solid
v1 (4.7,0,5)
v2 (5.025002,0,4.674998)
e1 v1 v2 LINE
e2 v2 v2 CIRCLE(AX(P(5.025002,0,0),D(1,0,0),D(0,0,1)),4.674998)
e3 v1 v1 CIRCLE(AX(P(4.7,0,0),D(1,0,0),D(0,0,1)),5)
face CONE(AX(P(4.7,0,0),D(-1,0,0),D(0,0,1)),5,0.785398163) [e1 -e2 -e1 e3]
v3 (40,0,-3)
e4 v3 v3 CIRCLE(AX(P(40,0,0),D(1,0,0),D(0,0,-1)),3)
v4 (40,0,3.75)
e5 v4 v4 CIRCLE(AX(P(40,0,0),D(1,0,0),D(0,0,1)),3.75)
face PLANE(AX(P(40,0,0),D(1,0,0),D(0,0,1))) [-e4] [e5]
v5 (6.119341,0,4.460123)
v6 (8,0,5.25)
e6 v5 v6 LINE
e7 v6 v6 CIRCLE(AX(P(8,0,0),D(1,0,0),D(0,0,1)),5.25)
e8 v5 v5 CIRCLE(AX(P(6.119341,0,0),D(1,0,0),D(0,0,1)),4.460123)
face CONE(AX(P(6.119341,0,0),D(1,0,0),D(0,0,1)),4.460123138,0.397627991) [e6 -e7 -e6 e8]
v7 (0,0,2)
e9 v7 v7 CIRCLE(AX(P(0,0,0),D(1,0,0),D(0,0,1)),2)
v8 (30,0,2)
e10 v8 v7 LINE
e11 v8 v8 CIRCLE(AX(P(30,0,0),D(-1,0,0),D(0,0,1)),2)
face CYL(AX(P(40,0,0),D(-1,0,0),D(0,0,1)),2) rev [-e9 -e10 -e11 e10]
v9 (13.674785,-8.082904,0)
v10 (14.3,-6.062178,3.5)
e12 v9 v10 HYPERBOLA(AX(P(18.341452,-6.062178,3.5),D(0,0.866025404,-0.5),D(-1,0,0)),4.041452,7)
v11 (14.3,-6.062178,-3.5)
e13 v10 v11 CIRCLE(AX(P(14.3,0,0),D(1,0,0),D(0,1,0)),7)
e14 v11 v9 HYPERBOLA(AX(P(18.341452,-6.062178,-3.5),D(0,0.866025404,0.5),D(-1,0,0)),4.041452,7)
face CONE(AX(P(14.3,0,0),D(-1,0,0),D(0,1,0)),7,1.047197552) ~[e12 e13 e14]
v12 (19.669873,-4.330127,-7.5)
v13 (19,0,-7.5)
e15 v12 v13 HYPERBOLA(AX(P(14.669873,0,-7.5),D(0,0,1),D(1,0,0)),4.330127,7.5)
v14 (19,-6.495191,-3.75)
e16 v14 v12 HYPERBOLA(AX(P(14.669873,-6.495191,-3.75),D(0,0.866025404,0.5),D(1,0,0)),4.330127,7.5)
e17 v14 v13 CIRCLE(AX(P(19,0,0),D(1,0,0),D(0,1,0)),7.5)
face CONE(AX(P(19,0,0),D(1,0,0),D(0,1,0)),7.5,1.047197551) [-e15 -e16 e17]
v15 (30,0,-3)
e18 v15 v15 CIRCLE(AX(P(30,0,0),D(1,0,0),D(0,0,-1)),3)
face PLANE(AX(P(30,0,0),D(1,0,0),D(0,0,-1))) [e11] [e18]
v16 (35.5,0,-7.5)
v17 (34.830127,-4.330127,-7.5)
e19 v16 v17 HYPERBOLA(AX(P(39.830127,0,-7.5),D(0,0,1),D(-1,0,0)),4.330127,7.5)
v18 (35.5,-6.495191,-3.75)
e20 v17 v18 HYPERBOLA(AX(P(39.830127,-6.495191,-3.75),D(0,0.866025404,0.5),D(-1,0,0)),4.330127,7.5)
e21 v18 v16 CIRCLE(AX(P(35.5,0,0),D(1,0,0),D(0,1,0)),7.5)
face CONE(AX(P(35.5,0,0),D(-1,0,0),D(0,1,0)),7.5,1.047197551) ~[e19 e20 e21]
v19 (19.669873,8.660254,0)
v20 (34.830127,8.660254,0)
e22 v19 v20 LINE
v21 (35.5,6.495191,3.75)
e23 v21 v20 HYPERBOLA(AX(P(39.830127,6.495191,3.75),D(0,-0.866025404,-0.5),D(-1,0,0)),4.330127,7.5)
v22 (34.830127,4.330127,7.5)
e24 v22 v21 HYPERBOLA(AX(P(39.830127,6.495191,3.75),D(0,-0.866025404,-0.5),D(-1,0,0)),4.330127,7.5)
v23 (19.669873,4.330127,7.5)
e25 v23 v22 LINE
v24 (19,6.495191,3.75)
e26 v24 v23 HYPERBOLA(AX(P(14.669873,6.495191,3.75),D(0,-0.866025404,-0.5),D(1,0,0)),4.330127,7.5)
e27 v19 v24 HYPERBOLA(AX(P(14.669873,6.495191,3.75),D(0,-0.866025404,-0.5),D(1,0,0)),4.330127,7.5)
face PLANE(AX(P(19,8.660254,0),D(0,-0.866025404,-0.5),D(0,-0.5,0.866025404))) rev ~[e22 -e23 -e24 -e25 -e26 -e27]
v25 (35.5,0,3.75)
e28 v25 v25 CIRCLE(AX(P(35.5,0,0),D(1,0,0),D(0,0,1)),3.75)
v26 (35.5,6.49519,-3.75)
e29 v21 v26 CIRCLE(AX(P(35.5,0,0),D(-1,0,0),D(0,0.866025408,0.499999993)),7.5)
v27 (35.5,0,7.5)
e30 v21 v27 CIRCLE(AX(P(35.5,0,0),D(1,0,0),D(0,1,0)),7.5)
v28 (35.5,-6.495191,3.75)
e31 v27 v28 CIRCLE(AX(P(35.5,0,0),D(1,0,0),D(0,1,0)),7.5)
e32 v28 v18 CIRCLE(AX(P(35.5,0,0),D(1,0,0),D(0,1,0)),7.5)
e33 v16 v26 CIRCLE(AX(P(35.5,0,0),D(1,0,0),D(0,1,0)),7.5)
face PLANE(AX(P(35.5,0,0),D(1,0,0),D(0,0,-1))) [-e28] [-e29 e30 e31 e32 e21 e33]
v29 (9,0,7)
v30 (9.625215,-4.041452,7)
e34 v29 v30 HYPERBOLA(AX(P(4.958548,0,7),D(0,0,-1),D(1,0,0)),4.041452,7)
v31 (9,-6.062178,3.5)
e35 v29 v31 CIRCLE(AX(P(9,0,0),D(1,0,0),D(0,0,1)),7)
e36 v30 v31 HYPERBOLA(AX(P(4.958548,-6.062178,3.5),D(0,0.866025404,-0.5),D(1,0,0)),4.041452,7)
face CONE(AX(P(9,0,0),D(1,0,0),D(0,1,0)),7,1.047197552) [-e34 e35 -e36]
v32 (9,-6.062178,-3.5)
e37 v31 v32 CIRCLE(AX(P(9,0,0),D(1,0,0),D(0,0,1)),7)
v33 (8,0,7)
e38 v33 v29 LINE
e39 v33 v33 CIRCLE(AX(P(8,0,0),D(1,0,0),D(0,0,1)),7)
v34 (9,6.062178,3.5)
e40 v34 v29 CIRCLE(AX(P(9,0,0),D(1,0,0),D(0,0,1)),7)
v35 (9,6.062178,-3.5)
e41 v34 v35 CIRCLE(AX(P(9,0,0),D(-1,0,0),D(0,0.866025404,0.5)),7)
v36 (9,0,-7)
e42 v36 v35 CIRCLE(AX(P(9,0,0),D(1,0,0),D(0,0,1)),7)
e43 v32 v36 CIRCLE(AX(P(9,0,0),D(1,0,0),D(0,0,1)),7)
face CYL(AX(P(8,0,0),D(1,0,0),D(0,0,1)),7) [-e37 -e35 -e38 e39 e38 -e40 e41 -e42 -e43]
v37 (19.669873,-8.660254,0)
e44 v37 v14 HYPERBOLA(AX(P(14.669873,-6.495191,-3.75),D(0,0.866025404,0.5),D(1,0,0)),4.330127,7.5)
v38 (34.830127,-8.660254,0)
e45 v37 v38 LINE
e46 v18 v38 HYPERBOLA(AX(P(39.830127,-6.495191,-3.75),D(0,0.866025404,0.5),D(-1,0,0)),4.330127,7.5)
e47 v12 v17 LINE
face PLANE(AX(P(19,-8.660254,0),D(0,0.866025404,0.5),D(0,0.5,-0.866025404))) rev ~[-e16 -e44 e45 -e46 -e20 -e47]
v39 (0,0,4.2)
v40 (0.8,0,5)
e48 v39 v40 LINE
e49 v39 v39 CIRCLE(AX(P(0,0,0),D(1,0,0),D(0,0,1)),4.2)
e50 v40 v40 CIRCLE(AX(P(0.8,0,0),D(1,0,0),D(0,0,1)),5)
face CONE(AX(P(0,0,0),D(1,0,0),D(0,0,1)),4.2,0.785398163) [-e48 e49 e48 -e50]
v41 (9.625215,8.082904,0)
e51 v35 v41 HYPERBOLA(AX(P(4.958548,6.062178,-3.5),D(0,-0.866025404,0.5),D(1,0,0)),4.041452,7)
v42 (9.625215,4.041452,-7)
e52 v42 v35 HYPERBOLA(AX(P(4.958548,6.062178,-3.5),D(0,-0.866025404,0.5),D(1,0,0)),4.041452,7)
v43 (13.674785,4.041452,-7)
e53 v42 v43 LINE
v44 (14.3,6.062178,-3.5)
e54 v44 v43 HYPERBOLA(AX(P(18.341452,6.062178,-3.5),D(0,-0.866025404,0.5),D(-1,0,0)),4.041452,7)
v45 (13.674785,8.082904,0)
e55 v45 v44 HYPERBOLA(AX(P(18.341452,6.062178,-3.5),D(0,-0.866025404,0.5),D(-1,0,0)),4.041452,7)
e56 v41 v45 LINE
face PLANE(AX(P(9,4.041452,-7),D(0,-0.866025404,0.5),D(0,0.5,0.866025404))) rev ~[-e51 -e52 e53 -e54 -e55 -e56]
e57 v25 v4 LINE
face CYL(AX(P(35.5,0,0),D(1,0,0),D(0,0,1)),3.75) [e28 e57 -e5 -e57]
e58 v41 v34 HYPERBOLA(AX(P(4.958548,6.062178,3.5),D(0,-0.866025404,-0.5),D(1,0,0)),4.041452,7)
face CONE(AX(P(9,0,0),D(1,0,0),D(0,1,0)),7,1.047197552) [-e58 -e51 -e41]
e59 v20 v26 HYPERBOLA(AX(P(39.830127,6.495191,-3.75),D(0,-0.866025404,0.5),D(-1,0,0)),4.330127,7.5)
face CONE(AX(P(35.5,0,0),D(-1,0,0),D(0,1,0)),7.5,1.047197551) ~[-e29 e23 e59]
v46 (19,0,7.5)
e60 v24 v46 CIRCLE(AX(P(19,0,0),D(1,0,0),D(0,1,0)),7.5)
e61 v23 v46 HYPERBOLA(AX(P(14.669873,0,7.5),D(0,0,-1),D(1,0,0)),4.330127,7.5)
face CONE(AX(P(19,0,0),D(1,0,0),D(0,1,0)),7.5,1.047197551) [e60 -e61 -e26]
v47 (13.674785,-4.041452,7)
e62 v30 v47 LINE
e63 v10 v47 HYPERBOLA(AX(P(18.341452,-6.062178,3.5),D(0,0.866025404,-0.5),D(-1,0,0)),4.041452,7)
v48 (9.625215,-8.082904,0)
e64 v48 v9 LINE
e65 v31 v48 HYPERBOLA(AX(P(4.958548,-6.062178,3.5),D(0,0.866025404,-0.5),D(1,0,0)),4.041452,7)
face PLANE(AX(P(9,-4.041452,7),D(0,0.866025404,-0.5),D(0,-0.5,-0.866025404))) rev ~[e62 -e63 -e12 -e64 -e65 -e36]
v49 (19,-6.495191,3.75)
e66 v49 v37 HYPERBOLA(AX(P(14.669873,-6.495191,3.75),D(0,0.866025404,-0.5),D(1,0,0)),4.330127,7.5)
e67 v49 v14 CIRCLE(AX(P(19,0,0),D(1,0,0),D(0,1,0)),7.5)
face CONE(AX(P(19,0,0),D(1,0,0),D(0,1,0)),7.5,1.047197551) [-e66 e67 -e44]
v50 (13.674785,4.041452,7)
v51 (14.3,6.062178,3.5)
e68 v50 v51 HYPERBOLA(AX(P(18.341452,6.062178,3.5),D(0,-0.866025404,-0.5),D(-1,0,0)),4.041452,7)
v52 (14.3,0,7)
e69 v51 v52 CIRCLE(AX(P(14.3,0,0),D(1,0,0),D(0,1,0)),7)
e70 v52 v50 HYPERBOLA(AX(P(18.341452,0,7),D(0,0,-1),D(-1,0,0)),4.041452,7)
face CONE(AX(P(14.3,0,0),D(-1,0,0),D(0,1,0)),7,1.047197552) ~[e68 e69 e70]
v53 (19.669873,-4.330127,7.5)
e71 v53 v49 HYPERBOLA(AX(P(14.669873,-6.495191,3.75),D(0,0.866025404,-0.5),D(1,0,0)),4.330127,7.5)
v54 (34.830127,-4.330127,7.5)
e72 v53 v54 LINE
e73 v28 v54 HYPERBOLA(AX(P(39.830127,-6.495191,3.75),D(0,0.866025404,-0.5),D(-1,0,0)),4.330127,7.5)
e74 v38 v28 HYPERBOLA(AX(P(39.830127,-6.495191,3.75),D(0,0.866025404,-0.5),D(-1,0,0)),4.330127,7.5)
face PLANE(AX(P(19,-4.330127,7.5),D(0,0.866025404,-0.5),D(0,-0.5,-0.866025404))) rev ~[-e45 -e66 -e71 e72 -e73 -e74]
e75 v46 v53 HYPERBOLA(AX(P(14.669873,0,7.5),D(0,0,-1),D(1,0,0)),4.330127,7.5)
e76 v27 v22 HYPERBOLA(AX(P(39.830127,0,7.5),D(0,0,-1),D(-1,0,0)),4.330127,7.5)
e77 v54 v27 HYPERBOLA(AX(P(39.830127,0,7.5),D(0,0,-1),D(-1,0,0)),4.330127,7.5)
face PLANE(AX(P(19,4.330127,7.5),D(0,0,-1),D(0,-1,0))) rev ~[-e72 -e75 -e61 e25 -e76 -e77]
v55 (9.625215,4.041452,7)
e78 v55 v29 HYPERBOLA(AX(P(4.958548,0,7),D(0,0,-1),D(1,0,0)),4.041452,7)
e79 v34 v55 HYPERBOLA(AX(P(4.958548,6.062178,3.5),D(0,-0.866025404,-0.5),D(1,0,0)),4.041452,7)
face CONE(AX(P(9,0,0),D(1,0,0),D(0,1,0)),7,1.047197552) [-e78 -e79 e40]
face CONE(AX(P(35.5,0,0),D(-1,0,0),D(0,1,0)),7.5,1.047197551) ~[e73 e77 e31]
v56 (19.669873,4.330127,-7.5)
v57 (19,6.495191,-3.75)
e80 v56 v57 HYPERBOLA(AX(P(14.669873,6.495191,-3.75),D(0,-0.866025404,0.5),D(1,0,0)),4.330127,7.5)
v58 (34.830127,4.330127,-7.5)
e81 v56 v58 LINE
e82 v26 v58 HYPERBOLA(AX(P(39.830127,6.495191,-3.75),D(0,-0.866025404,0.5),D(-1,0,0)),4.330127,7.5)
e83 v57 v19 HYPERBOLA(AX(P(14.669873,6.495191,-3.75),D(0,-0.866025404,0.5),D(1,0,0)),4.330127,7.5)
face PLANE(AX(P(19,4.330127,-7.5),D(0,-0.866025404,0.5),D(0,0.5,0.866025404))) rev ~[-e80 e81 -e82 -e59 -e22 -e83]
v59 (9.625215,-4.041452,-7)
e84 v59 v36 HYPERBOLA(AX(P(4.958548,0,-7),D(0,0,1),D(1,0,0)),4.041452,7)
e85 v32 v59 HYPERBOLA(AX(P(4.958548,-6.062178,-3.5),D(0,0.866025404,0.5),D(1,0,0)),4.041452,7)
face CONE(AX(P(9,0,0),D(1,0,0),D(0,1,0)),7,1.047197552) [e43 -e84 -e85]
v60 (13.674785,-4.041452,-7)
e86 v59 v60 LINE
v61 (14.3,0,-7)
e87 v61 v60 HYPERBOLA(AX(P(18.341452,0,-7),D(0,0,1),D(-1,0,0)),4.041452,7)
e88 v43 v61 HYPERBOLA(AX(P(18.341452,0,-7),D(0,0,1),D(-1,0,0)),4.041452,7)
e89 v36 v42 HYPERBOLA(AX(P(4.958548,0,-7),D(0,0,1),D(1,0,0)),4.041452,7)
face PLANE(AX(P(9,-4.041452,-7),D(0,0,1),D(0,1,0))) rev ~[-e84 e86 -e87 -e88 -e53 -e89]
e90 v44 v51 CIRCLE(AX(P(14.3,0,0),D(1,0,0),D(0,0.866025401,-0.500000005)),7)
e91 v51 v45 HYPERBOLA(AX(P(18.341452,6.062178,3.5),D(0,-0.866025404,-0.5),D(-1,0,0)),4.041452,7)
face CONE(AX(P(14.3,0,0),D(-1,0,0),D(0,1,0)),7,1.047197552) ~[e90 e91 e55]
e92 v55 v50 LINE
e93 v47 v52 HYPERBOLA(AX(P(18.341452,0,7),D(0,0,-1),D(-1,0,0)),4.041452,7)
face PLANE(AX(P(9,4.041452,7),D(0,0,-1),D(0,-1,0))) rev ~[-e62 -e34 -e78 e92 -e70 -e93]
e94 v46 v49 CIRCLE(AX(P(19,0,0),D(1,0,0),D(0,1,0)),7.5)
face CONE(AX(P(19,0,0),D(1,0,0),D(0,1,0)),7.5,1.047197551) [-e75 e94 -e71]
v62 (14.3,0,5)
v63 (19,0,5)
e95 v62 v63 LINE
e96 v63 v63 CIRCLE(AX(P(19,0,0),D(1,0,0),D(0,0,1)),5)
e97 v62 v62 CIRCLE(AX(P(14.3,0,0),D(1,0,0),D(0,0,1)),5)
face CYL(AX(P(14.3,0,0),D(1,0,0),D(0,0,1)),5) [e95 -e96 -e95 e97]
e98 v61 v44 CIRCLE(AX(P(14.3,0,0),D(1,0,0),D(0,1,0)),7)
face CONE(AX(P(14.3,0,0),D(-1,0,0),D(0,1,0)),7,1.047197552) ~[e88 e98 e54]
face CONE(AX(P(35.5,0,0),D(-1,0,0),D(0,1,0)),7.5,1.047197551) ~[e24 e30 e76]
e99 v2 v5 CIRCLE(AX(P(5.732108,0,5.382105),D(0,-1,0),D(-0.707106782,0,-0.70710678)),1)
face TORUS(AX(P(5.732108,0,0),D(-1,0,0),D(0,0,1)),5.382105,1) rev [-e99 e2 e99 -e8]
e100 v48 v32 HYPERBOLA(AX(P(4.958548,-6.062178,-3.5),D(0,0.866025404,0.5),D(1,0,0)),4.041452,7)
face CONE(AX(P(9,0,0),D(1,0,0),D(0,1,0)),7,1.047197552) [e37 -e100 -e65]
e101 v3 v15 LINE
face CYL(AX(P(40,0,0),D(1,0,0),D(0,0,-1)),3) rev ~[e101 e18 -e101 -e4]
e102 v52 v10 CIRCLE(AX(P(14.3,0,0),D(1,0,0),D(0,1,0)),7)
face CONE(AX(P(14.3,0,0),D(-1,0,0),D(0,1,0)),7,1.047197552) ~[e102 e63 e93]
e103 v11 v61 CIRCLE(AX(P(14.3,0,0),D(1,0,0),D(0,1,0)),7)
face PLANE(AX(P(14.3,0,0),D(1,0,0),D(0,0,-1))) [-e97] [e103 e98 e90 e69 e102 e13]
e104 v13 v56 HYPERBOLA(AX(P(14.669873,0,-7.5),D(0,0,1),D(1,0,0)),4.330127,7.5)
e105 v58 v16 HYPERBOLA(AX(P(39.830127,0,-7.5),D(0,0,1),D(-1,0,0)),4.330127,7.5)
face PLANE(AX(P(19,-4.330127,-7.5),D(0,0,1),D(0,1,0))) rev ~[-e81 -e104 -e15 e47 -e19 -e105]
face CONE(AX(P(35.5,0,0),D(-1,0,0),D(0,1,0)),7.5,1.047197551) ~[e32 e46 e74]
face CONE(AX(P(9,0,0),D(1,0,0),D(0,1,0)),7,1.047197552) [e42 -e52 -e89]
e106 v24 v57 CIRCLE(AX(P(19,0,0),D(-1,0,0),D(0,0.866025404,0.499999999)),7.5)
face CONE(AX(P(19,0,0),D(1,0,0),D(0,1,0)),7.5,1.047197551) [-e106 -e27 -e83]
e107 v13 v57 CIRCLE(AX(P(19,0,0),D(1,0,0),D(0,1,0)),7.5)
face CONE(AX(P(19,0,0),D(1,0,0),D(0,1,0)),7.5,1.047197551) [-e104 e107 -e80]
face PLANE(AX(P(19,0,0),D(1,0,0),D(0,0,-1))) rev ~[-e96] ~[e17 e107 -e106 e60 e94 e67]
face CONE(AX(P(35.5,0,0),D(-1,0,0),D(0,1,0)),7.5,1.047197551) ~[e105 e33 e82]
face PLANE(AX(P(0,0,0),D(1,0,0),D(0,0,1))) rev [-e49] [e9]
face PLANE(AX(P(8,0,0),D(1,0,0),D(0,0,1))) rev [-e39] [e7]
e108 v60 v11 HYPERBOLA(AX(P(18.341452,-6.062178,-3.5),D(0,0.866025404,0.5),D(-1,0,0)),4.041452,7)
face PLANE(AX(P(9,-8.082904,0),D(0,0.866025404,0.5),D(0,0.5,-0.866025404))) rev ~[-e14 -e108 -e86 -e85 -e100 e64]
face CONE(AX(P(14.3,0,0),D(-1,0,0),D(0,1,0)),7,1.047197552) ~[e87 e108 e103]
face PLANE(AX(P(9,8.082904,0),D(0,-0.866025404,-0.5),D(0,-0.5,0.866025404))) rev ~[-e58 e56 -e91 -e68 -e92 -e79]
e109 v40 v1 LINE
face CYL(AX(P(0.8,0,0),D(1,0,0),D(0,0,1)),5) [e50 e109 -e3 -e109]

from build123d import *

# Parameters (mm, degrees)
EXTRUDE_START       = -16.5
SKETCH_3_R          = 2
EXTRUDE_2_DEPTH     = 16.5
EXTRUDE_START_2     = -5.3
SKETCH_2_R          = 2
EXTRUDE_1_DEPTH     = 5.3
SKETCH_6_R          = 3
CUT_EXTRUDE_1_DEPTH = 10


with BuildPart() as part:
    # 草图1 → 旋转1 (revolve)
    with BuildSketch(Plane.XY, mode=Mode.PRIVATE) as revolve_1_sk:
        with BuildLine():
            Line((0, 2), (0, 4.2))
            Line((0, 4.2), (0.8, 5))
            Line((0.8, 5), (4.7, 5))
            Line((4.7, 5), (5.025001538, 4.674998462))
            ThreePointArc((5.025001538, 4.674998462), (5.539435688, 4.40084215), (6.119340804, 4.460123138))
            Line((6.119340804, 4.460123138), (8, 5.25))
            Line((8, 5.25), (8, 7))
            Line((8, 7), (9, 7))
            Line((9, 7), (14.3, 7))
            Line((14.3, 7), (14.3, 5))
            Line((14.3, 5), (19, 5))
            Line((19, 5), (19, 7.5))
            Line((19, 7.5), (35.5, 7.5))
            Line((35.5, 7.5), (35.5, 3.75))
            Line((35.5, 3.75), (40, 3.75))
            Line((40, 3.75), (40, 2))
            Line((40, 2), (0, 2))
        make_face()
    revolve(revolve_1_sk.sketch.rotate(Axis((0, 0, 0), (1, 0, 0)), 90), axis=Axis((0, 0, 0), (1, 0, 0)))

    # 草图3 → 拉伸2 (add)
    with BuildSketch(Plane(origin=(35.5, 0, 0), x_dir=(0, 0, -1), z_dir=(1, 0, 0)).offset(EXTRUDE_START)):
        Polygon((7.5, -4.330127019), (7.5, 4.330127019), (0, 8.660254038), (-7.5, 4.330127019), (-7.5, -4.330127019), (0, -8.660254038), align=None)
        with Locations(Location((0, 0, 0), (0, 0, 180))):
            Circle(SKETCH_3_R, mode=Mode.SUBTRACT)
    extrude(amount=EXTRUDE_2_DEPTH)

    # 草图2 → 凸台-拉伸1 (add)
    with BuildSketch(Plane(origin=(14.3, 0, 0), x_dir=(0, 0, -1), z_dir=(1, 0, 0)).offset(EXTRUDE_START_2)):
        Polygon((-7, 4.041451884), (-7, -4.041451884), (0, -8.082903769), (7, -4.041451884), (7, 4.041451884), (0, 8.082903769), align=None)
        with Locations(Location((0, 0, 0), (0, 0, 180))):
            Circle(SKETCH_2_R, mode=Mode.SUBTRACT)
    extrude(amount=EXTRUDE_1_DEPTH)

    # 草图4 → 切除-旋转1 (revolve, cut)
    with BuildSketch(Plane.XY):
        Polygon((9, 7), (9.625214782, 8.082903769), (9, 8.082903769), align=None)
        Polygon((14.3, 7), (13.674785218, 8.082903769), (14.3, 8.082903769), align=None)
        Polygon((19, 7.5), (19.669872981, 8.660254038), (19, 8.660254038), align=None)
        Polygon((35.5, 7.5), (34.830127019, 8.660254038), (35.5, 8.660254038), align=None)
    revolve(axis=Axis((0, 0, 0), (1, 0, 0)), mode=Mode.SUBTRACT)

    # 草图6 → 切除-拉伸1 (cut)
    with BuildSketch(Plane(origin=(40, 0, 0), x_dir=(0, 0, -1), z_dir=(1, 0, 0))):
        Circle(SKETCH_6_R)
    extrude(amount=-CUT_EXTRUDE_1_DEPTH, mode=Mode.SUBTRACT)


solid = part.part
